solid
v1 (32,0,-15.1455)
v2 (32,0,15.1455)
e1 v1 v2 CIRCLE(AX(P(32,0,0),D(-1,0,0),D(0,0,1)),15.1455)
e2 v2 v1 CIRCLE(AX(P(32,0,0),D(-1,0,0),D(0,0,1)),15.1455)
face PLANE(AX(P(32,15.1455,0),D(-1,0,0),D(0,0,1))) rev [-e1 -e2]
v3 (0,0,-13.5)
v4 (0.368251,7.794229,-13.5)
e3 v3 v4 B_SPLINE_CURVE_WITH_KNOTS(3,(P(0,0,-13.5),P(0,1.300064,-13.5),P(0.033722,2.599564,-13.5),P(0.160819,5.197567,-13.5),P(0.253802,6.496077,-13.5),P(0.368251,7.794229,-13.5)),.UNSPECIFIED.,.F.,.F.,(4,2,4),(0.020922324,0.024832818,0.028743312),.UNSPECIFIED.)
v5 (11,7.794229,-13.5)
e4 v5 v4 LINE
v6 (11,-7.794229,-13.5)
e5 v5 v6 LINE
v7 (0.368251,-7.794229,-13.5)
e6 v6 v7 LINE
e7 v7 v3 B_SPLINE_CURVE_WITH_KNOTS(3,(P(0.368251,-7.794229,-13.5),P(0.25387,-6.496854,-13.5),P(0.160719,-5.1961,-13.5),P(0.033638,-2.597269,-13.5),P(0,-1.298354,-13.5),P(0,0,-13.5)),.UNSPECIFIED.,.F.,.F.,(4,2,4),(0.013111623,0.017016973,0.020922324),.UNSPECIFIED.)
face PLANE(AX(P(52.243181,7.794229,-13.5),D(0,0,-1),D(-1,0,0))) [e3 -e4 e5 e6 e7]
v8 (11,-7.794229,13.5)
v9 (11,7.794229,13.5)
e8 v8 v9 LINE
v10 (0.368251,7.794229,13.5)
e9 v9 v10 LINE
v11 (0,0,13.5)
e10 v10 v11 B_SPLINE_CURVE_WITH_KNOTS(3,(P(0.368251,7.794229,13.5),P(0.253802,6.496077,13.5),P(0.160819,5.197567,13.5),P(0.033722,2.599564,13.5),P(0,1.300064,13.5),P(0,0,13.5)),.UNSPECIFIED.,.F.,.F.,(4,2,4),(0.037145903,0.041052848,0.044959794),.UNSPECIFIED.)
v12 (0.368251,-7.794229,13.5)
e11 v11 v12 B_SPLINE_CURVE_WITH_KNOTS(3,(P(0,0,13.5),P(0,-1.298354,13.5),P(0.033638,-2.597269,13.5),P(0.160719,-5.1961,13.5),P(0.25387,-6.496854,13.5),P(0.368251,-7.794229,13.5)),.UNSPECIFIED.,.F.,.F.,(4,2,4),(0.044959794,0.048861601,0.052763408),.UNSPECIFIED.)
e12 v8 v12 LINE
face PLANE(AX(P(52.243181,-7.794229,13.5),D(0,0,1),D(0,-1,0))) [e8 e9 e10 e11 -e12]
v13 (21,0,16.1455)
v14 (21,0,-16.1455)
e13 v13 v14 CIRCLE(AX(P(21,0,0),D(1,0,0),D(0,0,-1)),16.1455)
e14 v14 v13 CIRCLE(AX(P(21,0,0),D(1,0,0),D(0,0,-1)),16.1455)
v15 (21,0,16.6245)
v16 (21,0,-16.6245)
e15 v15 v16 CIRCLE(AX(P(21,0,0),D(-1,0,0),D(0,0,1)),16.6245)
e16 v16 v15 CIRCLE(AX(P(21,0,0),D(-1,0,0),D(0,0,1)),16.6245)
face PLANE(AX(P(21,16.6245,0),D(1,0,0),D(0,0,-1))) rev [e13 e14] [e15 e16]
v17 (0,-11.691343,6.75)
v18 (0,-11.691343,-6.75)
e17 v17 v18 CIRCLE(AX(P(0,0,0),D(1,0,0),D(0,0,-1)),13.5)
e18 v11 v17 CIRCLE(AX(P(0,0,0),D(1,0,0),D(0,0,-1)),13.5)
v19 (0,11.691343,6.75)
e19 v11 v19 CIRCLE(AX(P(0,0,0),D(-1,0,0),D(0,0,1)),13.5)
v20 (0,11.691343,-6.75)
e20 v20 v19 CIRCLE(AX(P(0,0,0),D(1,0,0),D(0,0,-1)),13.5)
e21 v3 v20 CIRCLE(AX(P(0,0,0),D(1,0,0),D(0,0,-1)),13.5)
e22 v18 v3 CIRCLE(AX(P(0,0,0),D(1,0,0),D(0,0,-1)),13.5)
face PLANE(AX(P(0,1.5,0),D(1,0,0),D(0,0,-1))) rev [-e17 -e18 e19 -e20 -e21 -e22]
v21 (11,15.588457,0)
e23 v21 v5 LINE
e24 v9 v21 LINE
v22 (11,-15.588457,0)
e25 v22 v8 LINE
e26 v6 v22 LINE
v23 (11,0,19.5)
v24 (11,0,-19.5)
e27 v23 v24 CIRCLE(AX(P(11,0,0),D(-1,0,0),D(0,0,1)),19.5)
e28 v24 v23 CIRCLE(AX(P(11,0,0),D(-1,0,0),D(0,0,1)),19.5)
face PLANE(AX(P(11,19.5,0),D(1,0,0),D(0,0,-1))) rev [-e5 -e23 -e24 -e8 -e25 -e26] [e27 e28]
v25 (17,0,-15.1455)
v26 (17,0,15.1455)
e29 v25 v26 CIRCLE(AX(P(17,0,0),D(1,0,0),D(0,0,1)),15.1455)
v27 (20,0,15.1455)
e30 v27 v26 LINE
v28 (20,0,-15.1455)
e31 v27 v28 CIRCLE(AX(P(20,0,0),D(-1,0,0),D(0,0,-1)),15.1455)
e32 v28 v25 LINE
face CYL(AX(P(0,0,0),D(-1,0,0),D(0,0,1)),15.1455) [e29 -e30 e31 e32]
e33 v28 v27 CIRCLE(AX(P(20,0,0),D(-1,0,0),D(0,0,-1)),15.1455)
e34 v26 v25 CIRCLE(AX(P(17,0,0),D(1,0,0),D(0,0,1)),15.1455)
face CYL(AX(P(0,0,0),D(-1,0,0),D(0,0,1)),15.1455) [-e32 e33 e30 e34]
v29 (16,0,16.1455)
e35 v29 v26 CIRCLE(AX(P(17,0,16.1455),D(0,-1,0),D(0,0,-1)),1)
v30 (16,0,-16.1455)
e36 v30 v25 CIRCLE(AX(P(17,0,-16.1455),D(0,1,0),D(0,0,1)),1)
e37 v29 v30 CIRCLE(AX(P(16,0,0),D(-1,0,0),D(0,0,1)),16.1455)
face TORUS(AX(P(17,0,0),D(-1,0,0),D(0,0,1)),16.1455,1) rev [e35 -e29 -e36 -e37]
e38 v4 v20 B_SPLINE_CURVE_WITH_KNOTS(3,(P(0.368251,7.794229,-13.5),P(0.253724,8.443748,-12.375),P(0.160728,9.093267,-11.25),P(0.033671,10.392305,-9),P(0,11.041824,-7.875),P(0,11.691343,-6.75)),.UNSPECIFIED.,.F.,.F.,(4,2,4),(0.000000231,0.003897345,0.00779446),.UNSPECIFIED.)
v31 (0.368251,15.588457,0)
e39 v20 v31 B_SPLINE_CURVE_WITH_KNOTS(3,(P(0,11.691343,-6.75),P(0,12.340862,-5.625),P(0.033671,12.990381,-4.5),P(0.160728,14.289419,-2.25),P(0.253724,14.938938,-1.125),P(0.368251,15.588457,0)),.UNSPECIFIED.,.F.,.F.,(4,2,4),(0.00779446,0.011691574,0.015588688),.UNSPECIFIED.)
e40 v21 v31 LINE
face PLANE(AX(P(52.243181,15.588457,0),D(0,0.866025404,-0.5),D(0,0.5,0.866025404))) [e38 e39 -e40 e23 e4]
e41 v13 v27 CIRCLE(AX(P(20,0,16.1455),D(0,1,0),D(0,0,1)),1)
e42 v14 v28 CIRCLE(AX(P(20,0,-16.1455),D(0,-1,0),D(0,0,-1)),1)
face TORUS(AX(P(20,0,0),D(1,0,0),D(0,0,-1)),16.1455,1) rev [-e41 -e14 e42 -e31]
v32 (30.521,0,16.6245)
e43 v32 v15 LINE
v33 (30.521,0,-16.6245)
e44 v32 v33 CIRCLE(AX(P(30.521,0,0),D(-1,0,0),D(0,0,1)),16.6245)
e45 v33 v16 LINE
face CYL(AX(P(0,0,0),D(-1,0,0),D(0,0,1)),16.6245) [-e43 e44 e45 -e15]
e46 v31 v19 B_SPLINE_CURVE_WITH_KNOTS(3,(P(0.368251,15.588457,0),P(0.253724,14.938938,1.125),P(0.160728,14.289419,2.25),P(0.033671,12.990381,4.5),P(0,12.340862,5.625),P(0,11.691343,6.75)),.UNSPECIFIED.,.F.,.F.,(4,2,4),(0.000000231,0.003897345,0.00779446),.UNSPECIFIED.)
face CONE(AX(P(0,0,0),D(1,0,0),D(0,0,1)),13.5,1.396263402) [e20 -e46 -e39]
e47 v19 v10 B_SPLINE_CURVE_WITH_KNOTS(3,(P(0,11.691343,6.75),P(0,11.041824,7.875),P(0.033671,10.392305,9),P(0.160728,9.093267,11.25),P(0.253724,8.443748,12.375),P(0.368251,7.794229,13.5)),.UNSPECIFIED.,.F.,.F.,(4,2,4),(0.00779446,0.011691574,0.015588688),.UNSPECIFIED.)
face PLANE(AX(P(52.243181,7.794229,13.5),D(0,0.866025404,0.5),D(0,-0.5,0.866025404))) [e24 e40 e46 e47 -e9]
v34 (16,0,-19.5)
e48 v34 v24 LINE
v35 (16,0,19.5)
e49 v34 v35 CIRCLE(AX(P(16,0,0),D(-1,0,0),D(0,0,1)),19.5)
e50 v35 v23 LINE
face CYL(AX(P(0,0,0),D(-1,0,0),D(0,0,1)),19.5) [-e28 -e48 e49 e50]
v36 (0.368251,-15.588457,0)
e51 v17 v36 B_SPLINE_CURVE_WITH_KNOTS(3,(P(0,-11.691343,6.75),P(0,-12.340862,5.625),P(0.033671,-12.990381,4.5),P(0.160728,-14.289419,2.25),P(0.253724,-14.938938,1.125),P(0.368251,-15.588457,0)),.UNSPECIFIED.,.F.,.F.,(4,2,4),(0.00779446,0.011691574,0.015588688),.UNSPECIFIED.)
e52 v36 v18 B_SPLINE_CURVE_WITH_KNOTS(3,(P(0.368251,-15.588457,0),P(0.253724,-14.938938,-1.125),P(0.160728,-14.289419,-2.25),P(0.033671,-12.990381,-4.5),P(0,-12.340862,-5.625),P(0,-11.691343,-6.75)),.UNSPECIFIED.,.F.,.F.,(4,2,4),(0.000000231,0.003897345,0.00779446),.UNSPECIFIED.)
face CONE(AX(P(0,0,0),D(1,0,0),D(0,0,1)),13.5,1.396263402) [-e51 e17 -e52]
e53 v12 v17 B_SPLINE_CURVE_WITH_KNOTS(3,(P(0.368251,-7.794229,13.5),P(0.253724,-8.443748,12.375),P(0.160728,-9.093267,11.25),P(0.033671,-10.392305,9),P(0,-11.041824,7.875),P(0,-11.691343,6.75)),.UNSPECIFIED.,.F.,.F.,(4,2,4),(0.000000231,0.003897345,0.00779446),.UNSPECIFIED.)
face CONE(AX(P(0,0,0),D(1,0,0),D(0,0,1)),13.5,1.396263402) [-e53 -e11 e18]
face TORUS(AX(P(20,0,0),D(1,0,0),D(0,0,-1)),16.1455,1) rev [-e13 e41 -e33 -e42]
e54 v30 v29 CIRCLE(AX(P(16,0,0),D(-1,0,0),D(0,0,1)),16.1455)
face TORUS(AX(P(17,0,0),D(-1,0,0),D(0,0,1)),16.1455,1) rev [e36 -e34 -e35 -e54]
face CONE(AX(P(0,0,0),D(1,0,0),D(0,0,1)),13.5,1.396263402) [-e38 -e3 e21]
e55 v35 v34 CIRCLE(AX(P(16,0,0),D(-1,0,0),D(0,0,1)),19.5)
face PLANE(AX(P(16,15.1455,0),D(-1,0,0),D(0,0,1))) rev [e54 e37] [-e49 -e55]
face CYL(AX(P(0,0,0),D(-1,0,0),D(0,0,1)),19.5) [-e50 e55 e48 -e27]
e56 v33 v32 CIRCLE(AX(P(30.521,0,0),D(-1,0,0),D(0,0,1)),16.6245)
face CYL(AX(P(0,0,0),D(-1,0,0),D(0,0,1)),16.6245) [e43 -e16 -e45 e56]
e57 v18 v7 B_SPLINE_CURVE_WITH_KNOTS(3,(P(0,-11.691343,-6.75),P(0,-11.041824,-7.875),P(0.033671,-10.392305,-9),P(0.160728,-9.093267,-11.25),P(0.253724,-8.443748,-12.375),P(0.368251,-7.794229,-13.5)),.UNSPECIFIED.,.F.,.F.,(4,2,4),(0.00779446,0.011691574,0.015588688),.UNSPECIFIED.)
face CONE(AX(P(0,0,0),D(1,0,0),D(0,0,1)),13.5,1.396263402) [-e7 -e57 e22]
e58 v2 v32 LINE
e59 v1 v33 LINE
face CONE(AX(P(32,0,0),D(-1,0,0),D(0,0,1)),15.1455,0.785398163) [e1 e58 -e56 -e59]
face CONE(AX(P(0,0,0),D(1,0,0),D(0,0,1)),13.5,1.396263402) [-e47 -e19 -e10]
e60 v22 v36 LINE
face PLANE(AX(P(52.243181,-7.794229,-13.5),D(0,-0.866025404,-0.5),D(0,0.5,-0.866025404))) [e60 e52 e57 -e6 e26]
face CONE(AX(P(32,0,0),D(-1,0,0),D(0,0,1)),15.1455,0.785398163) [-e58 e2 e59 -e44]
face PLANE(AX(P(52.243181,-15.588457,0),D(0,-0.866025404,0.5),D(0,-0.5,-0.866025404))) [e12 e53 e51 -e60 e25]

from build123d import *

# Parameters (mm, degrees)
EXTRUDE1_DEPTH     = 11
SKETCH3_OUTSIDE_W  = 167.178
SKETCH3_OUTSIDE_H  = 167.178
SKETCH3_OUTSIDE_R  = 13.5
CUT_EXTRUDE1_DEPTH = 10
CUT_EXTRUDE1_DRAFT = -80
FILLET1_R          = 1


with BuildPart() as part:
    # Sketch1 → Revolve1 (revolve)
    with BuildSketch(Plane.XY, mode=Mode.PRIVATE) as revolve1_sk:
        Polygon((21, 16.6245), (21, 15.1455), (16, 15.1455), (16, 19.5), (11, 19.5), (11, 1.5), (0, 1.5), (0, 0), (32, 0), (32, 15.1455), (30.521, 16.6245), align=None)
    revolve(revolve1_sk.sketch.rotate(Axis((0, 0, 0), (1, 0, 0)), 90), axis=Axis((0, 0, 0), (1, 0, 0)))

    # Sketch2 → Extrude1 (add)
    with BuildSketch(Plane.ZY):
        Polygon((0, 15.588457268), (-13.5, 7.794228634), (-13.5, -7.794228634), (0, -15.588457268), (13.5, -7.794228634), (13.5, 7.794228634), align=None)
    extrude(amount=-EXTRUDE1_DEPTH)


with BuildPart() as cut_extrude1_tool:
    # Sketch3 outside → Cut-Extrude1 (with draft: the straight prism first)
    with BuildSketch(Plane.ZY):
        Rectangle(SKETCH3_OUTSIDE_W, SKETCH3_OUTSIDE_H)
        Circle(SKETCH3_OUTSIDE_R, mode=Mode.SUBTRACT)
    extrude(amount=-CUT_EXTRUDE1_DEPTH)
    # Cut-Extrude1: the draft: its side faces are tilted about the plane it starts from
    cut_extrude1_sides = [cut_extrude1_tool.faces().sort_by_distance(p)[0] for p in [
        (5, -83.589, 0),
        (5, 0, 83.589),
        (5, 83.589, 0),
        (5, 0, -83.589),
        (5, 0, -13.5),
    ]]
    draft(cut_extrude1_sides, Plane.ZY, CUT_EXTRUDE1_DRAFT)


with BuildPart() as part_1:
    add(part.part)

    # Cut-Extrude1: cut by cut_extrude1_tool
    add(cut_extrude1_tool.part, mode=Mode.SUBTRACT)

    # Fillet1
    fillet1_edges = [part_1.edges().sort_by_distance(p)[0] for p in [
        (21, 0, -15.1455),
        (16, 0, -15.1455),
    ]]
    fillet(fillet1_edges, radius=FILLET1_R)


solid = part_1.part
